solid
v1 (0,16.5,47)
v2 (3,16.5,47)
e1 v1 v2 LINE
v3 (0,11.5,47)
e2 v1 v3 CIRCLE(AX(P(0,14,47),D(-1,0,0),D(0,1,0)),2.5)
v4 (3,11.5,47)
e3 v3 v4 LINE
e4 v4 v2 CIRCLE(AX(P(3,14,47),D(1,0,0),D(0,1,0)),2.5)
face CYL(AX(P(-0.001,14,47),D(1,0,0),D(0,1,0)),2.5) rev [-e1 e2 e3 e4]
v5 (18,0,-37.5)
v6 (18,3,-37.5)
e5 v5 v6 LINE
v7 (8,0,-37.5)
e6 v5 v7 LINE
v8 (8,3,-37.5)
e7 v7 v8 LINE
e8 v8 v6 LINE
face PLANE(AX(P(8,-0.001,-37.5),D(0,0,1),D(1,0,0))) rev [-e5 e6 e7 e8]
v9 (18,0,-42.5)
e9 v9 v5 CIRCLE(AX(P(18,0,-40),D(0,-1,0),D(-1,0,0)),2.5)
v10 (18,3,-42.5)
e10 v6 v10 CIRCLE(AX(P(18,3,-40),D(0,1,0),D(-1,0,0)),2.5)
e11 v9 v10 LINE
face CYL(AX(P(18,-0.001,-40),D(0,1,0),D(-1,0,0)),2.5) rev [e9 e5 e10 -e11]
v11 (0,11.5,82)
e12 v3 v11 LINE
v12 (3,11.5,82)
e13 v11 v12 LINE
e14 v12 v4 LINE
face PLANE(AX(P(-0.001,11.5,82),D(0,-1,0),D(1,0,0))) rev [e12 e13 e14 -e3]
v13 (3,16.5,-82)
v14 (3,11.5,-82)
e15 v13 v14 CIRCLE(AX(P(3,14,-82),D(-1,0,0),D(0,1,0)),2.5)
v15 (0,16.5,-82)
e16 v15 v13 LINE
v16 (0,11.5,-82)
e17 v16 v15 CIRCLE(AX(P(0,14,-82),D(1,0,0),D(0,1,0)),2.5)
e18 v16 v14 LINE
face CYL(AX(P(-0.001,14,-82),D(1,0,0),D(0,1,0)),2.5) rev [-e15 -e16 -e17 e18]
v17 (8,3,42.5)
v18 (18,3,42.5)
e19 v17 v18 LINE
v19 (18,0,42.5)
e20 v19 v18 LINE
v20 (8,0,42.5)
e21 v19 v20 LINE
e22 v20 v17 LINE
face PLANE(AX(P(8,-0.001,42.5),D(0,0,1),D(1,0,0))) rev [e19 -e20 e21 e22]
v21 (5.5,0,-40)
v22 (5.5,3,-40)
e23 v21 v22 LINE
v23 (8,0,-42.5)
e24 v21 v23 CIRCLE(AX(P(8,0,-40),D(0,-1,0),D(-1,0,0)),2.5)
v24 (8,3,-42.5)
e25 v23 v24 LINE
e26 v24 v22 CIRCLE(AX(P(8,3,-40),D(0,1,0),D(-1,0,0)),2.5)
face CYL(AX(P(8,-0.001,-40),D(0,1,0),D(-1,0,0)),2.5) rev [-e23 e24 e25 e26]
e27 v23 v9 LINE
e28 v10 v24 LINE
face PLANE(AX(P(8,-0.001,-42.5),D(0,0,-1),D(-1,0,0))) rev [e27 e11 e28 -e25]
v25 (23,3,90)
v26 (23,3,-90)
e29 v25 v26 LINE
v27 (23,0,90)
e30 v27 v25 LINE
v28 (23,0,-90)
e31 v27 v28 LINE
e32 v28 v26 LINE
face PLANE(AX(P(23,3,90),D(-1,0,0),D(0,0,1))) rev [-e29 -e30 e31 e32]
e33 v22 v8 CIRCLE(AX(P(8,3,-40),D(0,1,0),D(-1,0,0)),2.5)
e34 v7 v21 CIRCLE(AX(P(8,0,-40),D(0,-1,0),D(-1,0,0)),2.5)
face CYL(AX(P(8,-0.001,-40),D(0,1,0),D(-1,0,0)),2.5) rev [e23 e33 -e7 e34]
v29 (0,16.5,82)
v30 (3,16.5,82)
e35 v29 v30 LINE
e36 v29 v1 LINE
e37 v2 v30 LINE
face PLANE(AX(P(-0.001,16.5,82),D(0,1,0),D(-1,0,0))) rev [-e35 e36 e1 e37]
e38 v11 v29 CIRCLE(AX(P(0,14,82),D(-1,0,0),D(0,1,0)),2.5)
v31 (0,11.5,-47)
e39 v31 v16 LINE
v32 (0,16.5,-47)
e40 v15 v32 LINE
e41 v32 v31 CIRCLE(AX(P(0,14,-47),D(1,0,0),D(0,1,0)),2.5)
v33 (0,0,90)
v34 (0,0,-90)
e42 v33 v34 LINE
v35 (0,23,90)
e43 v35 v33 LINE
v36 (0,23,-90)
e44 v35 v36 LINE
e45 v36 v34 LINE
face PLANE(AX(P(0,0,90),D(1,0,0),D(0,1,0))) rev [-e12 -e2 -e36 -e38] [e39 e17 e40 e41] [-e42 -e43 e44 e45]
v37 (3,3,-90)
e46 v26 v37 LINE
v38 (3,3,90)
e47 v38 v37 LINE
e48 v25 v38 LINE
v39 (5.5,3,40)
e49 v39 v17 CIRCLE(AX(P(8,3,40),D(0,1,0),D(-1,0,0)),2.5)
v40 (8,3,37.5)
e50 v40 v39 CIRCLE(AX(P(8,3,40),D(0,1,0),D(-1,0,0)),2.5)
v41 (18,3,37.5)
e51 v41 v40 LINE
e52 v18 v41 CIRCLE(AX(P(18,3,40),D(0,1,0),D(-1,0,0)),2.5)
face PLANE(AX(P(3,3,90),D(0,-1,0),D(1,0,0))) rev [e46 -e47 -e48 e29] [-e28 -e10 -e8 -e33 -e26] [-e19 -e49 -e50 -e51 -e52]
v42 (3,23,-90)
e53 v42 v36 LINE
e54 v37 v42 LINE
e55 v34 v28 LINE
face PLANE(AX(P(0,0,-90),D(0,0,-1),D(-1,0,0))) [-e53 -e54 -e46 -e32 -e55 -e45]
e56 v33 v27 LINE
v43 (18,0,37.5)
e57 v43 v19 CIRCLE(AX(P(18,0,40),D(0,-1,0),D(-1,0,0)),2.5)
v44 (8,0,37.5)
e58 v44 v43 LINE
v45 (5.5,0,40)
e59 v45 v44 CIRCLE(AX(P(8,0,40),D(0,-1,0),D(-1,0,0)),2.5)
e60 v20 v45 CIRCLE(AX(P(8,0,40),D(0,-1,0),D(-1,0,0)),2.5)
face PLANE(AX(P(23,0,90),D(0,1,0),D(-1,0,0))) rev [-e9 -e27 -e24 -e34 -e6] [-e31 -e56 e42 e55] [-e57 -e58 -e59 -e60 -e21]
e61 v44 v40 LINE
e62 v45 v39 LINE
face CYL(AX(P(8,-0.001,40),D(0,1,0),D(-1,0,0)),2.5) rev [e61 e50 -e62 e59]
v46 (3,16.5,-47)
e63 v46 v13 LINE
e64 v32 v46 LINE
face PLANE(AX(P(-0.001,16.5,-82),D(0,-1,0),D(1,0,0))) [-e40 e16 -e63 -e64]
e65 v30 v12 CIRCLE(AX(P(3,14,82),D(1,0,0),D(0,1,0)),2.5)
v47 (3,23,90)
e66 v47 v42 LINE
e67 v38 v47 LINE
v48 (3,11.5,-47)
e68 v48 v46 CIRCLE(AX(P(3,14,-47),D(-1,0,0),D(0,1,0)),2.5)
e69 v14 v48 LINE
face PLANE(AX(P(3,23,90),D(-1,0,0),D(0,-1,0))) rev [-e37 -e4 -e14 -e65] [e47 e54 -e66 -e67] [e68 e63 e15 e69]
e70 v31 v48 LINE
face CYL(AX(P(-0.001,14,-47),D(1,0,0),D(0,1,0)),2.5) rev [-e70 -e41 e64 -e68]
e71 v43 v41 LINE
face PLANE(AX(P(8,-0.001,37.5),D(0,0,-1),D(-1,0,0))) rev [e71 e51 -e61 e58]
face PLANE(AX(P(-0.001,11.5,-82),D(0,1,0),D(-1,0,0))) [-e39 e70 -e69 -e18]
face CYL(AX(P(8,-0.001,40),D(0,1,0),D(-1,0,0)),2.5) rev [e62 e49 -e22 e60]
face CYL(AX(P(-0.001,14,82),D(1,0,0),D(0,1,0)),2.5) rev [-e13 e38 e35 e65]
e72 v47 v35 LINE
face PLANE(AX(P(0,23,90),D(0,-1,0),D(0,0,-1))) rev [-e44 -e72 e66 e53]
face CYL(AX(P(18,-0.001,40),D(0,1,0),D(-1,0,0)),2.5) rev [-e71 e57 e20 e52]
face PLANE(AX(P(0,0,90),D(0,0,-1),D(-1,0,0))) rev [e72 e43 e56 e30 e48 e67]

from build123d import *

# Parameters (mm, degrees)
EXTRUDE_1_DEPTH     = 90
CUT_EXTRUDE_1_REACH = 97.021
CUT_EXTRUDE_2_REACH = 97.021


with BuildPart() as part:
    # 草图1 → 凸台-拉伸1 (new, symmetric)
    with BuildSketch(Plane.XY):
        Polygon((0, 0), (0, 23), (3, 23), (3, 3), (23, 3), (23, 0), align=None)
    extrude(amount=EXTRUDE_1_DEPTH, both=True)

    # 草图3 → 切除-拉伸1 (cut, up to next)
    with BuildSketch(Plane(origin=(3, 0, 0), x_dir=(0, 0, -1), z_dir=(1, 0, 0)), mode=Mode.PRIVATE) as cut_extrude_1_sk1:
        with BuildLine():
            Line((-82, 16.5), (-47, 16.5))
            ThreePointArc((-47, 16.5), (-44.5, 14), (-47, 11.5))
            Line((-47, 11.5), (-82, 11.5))
            ThreePointArc((-82, 11.5), (-84.5, 14), (-82, 16.5))
        make_face()
    cut_extrude_1_tool1 = extrude(cut_extrude_1_sk1.sketch, amount=-CUT_EXTRUDE_1_REACH, mode=Mode.PRIVATE) & part.part
    cut_extrude_1 = cut_extrude_1_tool1.solids().sort_by_distance((3, 14, 64.5))[0]
    add(cut_extrude_1, mode=Mode.SUBTRACT)

    # 镜向1: 切除-拉伸1 across plane
    add(cut_extrude_1.mirror(Plane.XY), mode=Mode.SUBTRACT)

    # 草图4 → 切除-拉伸2 (cut, up to next)
    with BuildSketch(Plane(origin=(0, 3, 0), x_dir=(1, 0, 0), z_dir=(0, 1, 0)), mode=Mode.PRIVATE) as cut_extrude_2_sk1:
        with BuildLine():
            Line((8, 42.5), (18, 42.5))
            ThreePointArc((18, 42.5), (20.5, 40), (18, 37.5))
            Line((18, 37.5), (8, 37.5))
            ThreePointArc((8, 37.5), (5.5, 40), (8, 42.5))
        make_face()
    cut_extrude_2_tool1 = extrude(cut_extrude_2_sk1.sketch, amount=-CUT_EXTRUDE_2_REACH, mode=Mode.PRIVATE) & part.part
    # 草图4 → 切除-拉伸2 (cut, up to next)
    with BuildSketch(Plane(origin=(0, 3, 0), x_dir=(1, 0, 0), z_dir=(0, 1, 0)), mode=Mode.PRIVATE) as cut_extrude_2_sk2:
        with BuildLine():
            Line((8, -37.5), (18, -37.5))
            ThreePointArc((18, -37.5), (20.5, -40), (18, -42.5))
            Line((18, -42.5), (8, -42.5))
            ThreePointArc((8, -42.5), (5.5, -40), (8, -37.5))
        make_face()
    cut_extrude_2_tool2 = extrude(cut_extrude_2_sk2.sketch, amount=-CUT_EXTRUDE_2_REACH, mode=Mode.PRIVATE) & part.part
    add(cut_extrude_2_tool1.solids().sort_by_distance((13, 3, -40))[0], mode=Mode.SUBTRACT)
    add(cut_extrude_2_tool2.solids().sort_by_distance((13, 3, 40))[0], mode=Mode.SUBTRACT)


solid = part.part
